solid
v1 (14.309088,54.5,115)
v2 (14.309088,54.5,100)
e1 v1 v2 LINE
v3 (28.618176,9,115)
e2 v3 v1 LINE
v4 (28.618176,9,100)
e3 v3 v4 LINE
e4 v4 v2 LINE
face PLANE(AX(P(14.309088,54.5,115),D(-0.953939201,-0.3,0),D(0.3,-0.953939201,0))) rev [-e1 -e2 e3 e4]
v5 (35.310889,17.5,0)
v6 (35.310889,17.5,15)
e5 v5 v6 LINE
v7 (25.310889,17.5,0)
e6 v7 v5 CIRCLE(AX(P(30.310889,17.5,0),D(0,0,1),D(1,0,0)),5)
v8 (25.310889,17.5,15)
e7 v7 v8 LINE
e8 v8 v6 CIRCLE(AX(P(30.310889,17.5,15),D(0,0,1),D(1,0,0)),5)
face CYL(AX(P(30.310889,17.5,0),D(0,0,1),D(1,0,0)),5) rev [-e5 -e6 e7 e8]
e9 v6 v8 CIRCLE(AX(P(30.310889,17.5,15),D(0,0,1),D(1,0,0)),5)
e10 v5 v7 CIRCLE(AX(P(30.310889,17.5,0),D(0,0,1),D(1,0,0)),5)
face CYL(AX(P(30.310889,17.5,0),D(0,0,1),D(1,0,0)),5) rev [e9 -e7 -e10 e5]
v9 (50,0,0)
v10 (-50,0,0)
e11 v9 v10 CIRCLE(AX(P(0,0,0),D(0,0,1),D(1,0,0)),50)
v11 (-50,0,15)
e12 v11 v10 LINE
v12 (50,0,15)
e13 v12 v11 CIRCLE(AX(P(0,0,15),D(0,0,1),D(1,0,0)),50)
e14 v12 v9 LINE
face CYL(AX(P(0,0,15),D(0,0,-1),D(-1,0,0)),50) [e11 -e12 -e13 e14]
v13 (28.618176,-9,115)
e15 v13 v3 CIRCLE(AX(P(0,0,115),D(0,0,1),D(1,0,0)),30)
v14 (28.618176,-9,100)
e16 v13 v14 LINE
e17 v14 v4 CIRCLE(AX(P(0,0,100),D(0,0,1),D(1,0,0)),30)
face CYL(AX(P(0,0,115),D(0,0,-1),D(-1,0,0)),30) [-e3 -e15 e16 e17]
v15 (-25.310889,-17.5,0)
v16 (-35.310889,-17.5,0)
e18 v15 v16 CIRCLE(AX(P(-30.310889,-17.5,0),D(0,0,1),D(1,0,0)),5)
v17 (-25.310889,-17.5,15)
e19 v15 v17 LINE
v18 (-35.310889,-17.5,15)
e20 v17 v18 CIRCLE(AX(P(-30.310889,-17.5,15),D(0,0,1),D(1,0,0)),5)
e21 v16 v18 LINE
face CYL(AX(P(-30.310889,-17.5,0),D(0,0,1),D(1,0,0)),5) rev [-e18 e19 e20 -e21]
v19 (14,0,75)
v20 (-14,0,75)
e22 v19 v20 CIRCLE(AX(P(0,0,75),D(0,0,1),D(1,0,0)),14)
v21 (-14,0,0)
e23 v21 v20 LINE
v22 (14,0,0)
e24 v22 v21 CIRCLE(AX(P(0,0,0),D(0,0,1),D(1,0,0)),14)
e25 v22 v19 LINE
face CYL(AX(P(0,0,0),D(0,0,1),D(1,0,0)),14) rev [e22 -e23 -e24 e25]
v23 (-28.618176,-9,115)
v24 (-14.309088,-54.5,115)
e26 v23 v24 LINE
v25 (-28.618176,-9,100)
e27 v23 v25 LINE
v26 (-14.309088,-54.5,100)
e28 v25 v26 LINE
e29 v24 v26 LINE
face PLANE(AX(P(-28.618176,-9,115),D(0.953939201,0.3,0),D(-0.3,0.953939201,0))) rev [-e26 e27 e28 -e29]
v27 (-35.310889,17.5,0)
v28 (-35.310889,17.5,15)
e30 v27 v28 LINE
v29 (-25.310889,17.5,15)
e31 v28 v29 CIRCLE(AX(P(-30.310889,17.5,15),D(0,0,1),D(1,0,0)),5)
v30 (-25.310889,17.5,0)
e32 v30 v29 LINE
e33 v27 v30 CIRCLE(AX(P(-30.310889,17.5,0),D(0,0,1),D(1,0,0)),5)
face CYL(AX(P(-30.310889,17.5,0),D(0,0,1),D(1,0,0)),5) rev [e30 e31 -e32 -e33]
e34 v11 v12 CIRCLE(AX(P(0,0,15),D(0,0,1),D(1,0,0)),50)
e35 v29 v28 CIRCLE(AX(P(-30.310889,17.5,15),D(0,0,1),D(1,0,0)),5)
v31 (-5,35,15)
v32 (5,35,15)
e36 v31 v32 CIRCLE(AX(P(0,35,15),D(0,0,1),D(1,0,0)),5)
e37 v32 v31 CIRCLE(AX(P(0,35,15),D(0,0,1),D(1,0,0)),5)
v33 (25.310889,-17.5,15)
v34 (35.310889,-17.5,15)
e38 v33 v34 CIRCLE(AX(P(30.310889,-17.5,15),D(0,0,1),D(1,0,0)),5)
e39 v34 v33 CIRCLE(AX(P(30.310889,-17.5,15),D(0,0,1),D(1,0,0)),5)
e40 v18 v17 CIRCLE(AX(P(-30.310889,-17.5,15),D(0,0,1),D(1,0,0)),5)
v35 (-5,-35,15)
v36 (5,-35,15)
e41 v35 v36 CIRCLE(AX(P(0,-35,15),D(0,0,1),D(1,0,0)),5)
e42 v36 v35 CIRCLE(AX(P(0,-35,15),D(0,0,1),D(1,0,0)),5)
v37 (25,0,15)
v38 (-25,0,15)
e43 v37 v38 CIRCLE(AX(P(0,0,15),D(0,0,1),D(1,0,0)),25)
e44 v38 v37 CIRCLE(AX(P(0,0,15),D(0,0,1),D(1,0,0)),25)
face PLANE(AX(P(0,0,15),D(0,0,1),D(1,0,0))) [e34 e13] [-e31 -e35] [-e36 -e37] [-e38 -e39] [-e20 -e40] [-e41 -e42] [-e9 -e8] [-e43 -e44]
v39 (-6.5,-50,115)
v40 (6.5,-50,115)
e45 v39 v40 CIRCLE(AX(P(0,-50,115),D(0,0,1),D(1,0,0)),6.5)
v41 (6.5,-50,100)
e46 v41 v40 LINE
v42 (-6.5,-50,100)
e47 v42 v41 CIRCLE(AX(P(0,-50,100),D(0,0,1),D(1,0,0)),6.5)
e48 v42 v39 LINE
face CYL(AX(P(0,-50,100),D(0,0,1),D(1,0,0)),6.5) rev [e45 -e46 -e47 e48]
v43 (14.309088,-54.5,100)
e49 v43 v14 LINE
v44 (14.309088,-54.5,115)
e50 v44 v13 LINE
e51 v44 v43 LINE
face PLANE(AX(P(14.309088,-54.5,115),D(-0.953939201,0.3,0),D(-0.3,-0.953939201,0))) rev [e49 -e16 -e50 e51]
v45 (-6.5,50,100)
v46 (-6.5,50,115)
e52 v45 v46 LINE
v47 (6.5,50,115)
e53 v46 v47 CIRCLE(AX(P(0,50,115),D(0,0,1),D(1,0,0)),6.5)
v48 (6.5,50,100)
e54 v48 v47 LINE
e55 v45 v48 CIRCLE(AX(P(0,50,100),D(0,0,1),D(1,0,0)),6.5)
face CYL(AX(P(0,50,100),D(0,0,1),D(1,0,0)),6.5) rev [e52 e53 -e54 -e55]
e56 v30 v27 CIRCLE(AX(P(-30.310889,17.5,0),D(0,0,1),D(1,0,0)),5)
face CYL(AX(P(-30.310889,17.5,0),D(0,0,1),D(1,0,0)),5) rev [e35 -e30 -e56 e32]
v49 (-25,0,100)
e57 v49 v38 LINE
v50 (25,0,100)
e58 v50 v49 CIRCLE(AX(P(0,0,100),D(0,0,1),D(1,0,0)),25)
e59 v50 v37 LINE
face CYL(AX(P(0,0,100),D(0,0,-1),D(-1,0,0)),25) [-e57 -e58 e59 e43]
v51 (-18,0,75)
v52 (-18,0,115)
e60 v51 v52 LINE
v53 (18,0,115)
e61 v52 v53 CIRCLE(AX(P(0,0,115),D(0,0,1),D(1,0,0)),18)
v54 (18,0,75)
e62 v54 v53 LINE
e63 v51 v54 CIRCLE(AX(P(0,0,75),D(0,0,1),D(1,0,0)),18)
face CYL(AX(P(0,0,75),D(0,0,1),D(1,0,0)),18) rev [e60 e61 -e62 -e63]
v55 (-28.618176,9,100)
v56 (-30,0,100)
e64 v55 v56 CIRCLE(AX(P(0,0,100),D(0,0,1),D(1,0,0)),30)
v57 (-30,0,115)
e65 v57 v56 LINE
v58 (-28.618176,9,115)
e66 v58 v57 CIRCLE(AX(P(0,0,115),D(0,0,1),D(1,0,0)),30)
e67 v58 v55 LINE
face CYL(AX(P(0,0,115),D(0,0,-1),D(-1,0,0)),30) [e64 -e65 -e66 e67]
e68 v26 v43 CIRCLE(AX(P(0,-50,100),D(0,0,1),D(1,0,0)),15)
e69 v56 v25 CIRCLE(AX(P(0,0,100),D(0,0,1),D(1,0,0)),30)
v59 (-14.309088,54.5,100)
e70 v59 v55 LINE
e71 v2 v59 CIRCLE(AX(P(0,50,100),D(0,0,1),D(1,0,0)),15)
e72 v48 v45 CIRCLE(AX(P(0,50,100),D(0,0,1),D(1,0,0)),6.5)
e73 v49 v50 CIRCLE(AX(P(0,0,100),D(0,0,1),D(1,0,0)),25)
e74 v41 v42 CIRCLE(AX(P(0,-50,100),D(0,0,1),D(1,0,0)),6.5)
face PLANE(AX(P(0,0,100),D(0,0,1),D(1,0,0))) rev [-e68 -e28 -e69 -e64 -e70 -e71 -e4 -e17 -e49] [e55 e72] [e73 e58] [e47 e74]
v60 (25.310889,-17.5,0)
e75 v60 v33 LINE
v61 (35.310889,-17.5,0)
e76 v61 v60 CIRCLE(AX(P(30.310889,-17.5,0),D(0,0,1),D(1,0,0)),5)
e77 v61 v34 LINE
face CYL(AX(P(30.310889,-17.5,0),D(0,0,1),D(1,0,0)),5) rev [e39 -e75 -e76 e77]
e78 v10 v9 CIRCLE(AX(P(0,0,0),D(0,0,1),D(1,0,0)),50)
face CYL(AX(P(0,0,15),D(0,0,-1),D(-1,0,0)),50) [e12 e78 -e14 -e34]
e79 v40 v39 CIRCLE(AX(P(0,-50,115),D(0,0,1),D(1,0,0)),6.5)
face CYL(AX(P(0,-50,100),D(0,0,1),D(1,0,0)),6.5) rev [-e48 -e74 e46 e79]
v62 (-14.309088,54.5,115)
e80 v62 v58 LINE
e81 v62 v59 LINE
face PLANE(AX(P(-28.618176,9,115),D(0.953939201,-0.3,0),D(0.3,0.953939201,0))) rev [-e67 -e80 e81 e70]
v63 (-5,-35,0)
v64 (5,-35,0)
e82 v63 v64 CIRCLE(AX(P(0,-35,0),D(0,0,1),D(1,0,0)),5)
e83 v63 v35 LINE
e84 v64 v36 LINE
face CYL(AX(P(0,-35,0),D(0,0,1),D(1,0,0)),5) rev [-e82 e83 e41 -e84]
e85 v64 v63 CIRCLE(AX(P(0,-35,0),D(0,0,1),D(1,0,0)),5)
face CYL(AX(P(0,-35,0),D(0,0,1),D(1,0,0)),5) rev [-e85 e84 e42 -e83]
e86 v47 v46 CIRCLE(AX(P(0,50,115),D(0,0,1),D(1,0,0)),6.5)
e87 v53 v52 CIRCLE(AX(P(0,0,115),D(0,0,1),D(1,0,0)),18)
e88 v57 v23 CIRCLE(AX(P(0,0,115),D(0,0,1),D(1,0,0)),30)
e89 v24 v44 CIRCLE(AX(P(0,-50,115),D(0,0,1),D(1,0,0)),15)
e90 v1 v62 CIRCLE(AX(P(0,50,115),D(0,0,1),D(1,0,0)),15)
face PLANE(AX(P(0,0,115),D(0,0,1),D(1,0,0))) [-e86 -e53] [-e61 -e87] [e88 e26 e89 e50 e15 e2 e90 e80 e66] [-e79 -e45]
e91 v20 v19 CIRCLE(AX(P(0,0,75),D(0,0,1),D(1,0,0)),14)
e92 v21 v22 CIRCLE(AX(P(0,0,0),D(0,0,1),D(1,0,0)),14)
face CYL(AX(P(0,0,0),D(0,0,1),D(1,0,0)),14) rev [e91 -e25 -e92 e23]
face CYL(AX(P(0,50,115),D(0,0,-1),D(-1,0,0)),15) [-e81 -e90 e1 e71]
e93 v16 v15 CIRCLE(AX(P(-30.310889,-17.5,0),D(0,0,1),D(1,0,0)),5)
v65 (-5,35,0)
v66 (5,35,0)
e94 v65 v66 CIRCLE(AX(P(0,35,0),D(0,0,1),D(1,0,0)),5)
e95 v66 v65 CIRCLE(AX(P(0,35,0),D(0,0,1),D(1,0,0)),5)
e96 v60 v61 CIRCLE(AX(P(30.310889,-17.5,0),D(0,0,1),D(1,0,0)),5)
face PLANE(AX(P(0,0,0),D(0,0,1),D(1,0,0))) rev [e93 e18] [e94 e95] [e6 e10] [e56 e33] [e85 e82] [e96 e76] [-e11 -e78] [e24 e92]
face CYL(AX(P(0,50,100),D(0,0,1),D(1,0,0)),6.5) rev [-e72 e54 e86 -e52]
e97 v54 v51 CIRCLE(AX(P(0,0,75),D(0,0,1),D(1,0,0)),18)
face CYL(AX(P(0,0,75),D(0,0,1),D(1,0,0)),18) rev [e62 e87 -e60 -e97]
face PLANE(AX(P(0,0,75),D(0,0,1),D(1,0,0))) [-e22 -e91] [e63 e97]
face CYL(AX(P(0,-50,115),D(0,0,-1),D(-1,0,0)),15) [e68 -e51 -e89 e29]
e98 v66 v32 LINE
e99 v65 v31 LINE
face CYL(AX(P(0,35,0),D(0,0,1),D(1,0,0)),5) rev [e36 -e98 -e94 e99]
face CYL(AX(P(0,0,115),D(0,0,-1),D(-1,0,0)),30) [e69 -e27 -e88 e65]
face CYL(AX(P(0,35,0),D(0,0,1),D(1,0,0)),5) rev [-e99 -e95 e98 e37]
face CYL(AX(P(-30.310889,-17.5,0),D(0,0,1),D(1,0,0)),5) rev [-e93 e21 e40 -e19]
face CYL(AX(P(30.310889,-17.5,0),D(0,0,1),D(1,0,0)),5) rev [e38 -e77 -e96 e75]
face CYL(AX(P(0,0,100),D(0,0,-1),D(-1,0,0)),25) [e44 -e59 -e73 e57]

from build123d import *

# Parameters (mm, degrees)
ROUND_FLANGE_SKETCH_R            = 50
ROUND_FLANGE_100_DEPTH           = 15
ROUND_FLANGE_BOLT_HOLES_SKETCH_R = 5
ROUND_FLANGE_BOLT_HOLES_DEPTH    = 15
SPOOL_CORE_SKETCH_R              = 18
SPOOL_CORE_36_DEPTH              = 85
CORE_START                       = -85
CORE_BORE_SKETCH_R               = 18
CORE_BORE_36_DEPTH               = 85
SPOOL_PIPE_SKETCH_R              = 25
SPOOL_PIPE_50_DEPTH              = 85
OVAL_FLANGE_DEPTH                = 15
OVAL_FLANGE_HOLES_SKETCH_R       = 6.5
OVAL_FLANGE_HOLES_2X_13_DEPTH    = 15
OVAL_FLANGE_BORE_SKETCH_R        = 18
OVAL_FLANGE_BORE_36_DEPTH        = 40
THROUGH_BORE_SKETCH_R            = 14
THROUGH_BORE_28_DEPTH            = 75


with BuildPart() as part:
    # Round Flange Sketch → Round Flange Ø100 (new body)
    with BuildSketch(Plane.XY):
        Circle(ROUND_FLANGE_SKETCH_R)
    extrude(amount=ROUND_FLANGE_100_DEPTH)

    # Round Flange Bolt Holes Sketch → Round Flange Bolt Holes (cut)
    with BuildSketch(Plane.XY.offset(15)):
        with Locations((-30.310889132, 17.5)):
            Circle(ROUND_FLANGE_BOLT_HOLES_SKETCH_R)
        with Locations((0, 35)):
            Circle(ROUND_FLANGE_BOLT_HOLES_SKETCH_R)
        with Locations((30.310889132, 17.5)):
            Circle(ROUND_FLANGE_BOLT_HOLES_SKETCH_R)
        with Locations((-30.310889132, -17.5)):
            Circle(ROUND_FLANGE_BOLT_HOLES_SKETCH_R)
        with Locations((30.310889132, -17.5)):
            Circle(ROUND_FLANGE_BOLT_HOLES_SKETCH_R)
        with Locations((0, -35)):
            Circle(ROUND_FLANGE_BOLT_HOLES_SKETCH_R)
    extrude(amount=-ROUND_FLANGE_BOLT_HOLES_DEPTH, mode=Mode.SUBTRACT)

    # Spool Core Sketch → Spool Core Ø36 (add)
    with BuildSketch(Plane.XY.offset(15)):
        Circle(SPOOL_CORE_SKETCH_R)
    extrude(amount=SPOOL_CORE_36_DEPTH)

    # Core Bore Sketch → Core Bore Ø36 (cut)
    with BuildSketch(Plane.XY.offset(100).offset(CORE_START)):
        Circle(CORE_BORE_SKETCH_R)
    extrude(amount=CORE_BORE_36_DEPTH, mode=Mode.SUBTRACT)

    # Spool Pipe Sketch → Spool Pipe Ø50 (add)
    with BuildSketch(Plane.XY.offset(15)):
        Circle(SPOOL_PIPE_SKETCH_R)
    extrude(amount=SPOOL_PIPE_50_DEPTH)

    # Oval Flange Sketch → Oval Flange (add)
    with BuildSketch(Plane.XY.offset(100)):
        with BuildLine():
            Line((-28.618176043, 9), (-14.309088021, 54.5))
            ThreePointArc((-14.309088021, 54.5), (0, 65), (14.309088021, 54.5))
            Line((14.309088021, 54.5), (28.618176043, 9))
            ThreePointArc((28.618176043, 9), (30, 0), (28.618176043, -9))
            Line((28.618176043, -9), (14.309088021, -54.5))
            ThreePointArc((14.309088021, -54.5), (0, -65), (-14.309088021, -54.5))
            Line((-14.309088021, -54.5), (-28.618176043, -9))
            ThreePointArc((-28.618176043, -9), (-30, 0), (-28.618176043, 9))
        make_face()
    extrude(amount=OVAL_FLANGE_DEPTH)

    # Oval Flange Holes Sketch → Oval Flange Holes 2xØ13 (cut)
    with BuildSketch(Plane.XY.offset(115)):
        with Locations((0, 50)):
            Circle(OVAL_FLANGE_HOLES_SKETCH_R)
        with Locations((0, -50)):
            Circle(OVAL_FLANGE_HOLES_SKETCH_R)
    extrude(amount=-OVAL_FLANGE_HOLES_2X_13_DEPTH, mode=Mode.SUBTRACT)

    # Oval Flange Bore Sketch → Oval Flange Bore Ø36 (cut)
    with BuildSketch(Plane.XY.offset(115)):
        Circle(OVAL_FLANGE_BORE_SKETCH_R)
    extrude(amount=-OVAL_FLANGE_BORE_36_DEPTH, mode=Mode.SUBTRACT)

    # Through Bore Sketch → Through Bore Ø28 (cut)
    with BuildSketch(Plane.XY.offset(75)):
        Circle(THROUGH_BORE_SKETCH_R)
    extrude(amount=-THROUGH_BORE_28_DEPTH, mode=Mode.SUBTRACT)


solid = part.part
